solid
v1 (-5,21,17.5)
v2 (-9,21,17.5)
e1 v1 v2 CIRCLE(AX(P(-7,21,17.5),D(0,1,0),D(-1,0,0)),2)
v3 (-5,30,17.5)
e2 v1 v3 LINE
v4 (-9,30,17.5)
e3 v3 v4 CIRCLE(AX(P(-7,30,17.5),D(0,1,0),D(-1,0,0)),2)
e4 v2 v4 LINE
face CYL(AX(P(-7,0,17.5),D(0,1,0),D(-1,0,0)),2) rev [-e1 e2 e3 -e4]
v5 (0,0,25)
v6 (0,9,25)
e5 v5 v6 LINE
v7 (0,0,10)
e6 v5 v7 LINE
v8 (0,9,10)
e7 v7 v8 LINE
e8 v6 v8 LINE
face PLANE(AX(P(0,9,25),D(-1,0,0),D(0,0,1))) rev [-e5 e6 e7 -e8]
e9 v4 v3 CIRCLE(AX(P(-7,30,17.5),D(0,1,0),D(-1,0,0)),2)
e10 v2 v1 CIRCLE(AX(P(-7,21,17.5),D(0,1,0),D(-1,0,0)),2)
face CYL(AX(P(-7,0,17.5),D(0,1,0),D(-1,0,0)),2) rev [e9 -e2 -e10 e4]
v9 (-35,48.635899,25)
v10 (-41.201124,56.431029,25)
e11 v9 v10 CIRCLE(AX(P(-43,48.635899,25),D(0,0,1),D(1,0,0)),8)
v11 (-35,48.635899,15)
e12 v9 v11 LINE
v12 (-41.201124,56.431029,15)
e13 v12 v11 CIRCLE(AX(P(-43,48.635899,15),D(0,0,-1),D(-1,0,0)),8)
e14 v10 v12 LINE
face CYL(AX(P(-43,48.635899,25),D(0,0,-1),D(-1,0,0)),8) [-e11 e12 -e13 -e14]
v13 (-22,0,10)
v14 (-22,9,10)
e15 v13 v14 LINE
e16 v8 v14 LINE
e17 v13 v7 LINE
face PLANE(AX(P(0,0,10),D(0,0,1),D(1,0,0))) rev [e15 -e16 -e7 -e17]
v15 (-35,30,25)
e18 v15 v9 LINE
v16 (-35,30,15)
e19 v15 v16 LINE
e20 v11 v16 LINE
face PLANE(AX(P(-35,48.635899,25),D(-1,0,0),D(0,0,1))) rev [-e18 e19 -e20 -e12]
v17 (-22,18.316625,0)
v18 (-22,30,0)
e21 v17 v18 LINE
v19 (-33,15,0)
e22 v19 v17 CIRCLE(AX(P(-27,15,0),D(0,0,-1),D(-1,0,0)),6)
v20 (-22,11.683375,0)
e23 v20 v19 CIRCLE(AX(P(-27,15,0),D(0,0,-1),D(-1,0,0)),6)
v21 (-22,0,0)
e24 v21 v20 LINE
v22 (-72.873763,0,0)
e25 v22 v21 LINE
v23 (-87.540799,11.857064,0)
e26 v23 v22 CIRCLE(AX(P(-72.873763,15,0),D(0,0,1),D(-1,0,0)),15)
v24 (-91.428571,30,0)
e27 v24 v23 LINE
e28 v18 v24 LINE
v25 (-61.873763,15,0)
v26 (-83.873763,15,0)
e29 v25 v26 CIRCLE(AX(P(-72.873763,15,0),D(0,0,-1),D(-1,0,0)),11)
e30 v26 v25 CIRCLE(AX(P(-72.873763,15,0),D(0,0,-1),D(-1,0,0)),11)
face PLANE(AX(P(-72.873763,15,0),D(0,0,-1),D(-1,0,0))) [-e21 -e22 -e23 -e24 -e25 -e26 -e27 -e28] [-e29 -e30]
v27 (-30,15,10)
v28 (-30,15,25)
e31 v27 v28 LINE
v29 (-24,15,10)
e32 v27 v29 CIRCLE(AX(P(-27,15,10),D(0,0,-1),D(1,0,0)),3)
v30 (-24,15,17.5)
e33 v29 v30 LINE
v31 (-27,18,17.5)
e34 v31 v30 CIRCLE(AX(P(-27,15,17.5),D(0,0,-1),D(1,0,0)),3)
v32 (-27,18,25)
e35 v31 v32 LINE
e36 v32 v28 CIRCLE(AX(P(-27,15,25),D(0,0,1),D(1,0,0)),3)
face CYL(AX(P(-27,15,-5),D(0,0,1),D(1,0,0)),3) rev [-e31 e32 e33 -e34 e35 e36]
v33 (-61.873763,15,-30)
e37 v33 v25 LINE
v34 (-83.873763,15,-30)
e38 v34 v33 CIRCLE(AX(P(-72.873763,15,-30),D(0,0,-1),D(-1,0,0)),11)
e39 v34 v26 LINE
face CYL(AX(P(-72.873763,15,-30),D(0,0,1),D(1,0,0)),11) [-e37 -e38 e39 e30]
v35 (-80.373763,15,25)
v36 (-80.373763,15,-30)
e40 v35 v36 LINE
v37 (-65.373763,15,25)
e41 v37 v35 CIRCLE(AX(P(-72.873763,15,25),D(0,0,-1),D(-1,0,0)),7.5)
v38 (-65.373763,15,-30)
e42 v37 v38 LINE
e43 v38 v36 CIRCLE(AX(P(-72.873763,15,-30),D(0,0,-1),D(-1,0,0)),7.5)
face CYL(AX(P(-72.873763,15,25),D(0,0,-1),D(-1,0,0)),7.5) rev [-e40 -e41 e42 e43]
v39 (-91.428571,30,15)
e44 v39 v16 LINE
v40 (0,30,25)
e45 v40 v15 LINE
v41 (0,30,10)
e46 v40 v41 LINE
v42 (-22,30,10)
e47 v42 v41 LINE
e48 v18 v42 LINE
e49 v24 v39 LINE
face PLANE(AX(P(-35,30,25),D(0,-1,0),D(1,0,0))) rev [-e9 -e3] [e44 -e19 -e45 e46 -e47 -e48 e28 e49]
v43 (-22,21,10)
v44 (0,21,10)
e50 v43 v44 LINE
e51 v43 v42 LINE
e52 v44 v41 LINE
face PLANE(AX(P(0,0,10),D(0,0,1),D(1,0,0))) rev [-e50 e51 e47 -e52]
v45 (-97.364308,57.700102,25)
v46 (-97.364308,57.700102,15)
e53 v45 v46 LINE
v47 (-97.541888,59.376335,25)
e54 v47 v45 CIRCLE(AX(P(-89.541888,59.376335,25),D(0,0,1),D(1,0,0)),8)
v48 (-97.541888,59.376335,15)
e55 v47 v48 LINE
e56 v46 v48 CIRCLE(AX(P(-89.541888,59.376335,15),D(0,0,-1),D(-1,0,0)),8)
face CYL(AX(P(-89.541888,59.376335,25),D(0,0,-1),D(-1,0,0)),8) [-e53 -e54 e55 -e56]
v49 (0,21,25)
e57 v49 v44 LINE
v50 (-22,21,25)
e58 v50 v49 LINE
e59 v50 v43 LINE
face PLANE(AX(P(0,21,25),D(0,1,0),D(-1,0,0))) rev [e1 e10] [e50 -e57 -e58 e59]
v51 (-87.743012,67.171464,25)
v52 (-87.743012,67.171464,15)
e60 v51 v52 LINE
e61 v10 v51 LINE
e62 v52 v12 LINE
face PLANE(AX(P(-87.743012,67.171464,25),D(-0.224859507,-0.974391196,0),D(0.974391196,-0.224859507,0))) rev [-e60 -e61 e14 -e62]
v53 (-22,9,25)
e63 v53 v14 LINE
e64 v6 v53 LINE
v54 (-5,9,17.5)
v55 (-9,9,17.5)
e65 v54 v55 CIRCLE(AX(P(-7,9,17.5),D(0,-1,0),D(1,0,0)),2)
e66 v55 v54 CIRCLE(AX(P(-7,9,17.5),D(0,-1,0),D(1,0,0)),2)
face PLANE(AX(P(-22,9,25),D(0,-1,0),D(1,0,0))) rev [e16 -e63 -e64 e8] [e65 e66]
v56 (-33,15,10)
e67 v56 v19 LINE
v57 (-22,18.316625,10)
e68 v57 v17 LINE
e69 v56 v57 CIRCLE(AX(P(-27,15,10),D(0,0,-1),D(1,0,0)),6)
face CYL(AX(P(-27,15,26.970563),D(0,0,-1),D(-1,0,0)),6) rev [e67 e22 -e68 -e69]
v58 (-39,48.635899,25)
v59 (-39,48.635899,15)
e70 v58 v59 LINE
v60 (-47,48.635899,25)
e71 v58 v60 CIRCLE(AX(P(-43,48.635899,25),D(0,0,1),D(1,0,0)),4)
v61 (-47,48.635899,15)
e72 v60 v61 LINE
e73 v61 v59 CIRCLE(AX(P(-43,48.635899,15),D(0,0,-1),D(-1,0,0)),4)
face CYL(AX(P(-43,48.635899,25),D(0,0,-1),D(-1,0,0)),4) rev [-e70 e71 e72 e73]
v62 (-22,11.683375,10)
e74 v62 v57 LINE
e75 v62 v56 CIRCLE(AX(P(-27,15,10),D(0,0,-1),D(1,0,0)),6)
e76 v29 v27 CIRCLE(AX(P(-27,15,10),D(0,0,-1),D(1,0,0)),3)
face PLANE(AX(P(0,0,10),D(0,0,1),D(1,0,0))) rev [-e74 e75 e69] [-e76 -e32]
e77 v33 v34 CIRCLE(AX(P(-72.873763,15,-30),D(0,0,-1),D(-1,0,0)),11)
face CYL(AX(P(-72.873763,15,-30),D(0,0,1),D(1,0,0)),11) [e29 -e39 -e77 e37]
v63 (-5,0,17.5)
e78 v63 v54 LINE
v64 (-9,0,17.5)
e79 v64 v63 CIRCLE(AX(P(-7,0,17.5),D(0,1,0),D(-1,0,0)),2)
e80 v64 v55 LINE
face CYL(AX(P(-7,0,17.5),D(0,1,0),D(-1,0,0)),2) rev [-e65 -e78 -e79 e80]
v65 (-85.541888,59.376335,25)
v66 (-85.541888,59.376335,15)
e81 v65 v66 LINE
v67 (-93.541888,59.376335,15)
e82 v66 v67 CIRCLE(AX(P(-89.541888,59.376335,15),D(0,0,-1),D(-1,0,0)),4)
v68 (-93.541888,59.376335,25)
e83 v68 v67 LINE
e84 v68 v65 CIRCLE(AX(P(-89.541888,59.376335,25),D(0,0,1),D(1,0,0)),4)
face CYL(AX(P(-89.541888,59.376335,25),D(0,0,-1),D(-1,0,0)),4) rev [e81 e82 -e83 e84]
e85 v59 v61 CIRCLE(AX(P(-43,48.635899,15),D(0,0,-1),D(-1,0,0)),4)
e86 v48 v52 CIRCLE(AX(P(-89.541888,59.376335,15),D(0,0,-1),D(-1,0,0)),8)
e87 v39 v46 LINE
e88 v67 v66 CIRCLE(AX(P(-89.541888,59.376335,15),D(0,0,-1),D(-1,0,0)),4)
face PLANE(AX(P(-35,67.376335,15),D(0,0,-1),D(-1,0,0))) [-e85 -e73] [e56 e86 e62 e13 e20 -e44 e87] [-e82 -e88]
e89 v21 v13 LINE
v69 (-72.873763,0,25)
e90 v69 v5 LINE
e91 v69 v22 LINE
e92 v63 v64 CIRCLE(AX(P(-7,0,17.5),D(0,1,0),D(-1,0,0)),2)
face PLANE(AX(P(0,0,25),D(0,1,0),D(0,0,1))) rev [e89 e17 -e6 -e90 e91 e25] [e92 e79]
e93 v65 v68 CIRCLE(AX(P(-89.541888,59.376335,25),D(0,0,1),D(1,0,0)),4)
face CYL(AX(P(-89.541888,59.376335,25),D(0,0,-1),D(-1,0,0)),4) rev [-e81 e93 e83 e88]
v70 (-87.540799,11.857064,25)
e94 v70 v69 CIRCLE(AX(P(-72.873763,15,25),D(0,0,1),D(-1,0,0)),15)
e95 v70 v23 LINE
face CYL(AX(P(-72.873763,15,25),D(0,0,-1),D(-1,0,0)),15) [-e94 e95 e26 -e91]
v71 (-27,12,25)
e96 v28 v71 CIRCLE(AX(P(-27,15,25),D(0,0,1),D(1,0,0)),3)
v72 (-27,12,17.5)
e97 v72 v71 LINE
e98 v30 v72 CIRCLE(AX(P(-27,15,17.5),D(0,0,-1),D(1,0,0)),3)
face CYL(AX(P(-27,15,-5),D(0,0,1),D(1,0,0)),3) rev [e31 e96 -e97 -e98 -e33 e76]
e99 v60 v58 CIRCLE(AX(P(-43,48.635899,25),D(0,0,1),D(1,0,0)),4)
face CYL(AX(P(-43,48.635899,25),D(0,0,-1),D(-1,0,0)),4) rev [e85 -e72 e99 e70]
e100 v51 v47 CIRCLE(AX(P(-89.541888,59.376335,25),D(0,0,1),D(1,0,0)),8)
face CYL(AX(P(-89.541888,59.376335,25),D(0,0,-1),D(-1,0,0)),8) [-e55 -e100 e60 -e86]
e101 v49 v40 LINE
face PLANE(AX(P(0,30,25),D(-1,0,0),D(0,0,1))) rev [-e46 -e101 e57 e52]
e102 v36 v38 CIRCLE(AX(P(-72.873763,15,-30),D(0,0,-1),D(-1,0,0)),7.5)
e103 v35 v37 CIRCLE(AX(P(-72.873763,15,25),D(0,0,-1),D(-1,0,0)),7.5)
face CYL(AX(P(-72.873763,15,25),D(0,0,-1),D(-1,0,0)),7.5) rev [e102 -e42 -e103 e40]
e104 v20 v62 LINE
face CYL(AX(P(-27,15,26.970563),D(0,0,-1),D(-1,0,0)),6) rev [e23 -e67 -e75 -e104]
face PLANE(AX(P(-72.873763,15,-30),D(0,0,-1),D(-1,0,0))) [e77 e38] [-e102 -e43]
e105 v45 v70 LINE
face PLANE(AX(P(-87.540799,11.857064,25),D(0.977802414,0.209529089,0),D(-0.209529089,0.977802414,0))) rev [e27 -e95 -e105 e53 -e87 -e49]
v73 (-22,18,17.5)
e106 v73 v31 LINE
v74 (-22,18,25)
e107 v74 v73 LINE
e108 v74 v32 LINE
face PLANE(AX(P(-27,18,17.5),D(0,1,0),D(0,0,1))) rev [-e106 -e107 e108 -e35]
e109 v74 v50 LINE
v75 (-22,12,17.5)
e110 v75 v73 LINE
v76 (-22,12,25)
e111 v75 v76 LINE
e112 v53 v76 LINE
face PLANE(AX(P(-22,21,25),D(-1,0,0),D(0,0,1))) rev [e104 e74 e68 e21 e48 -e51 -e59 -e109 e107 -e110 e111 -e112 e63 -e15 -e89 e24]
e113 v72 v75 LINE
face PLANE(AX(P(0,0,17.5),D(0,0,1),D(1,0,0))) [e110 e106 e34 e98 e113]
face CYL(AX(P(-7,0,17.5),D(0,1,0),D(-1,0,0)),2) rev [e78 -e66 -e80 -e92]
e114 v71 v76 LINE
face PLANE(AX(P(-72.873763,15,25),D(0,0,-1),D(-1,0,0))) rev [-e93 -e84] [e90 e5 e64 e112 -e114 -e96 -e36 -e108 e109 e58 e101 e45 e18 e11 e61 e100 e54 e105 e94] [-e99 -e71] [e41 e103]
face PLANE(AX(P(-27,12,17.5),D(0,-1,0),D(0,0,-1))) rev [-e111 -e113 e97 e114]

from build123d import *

# Parameters (mm, degrees)
BRACKET_PLATE_PROFILE_R     = 4
BRACKET_PLATE_DEPTH         = 25
FORK_SLOT_SKETCH_W          = 80.7543585
FORK_SLOT_SKETCH_H          = 21.257894267
FORK_SLOT_DEPTH             = 108.407683018
PIVOT_BOSS_SKETCH_R         = 11
PIVOT_BOSS_22_DEPTH         = 30
PIVOT_BORE_SKETCH_R         = 7.5
PIVOT_BORE_15_DEPTH         = 131.686611628
FORK_NOTCH_SKETCH_W         = 22
FORK_NOTCH_SKETCH_H         = 19.498267172
FORK_NOTCH_22X10_DEPTH      = 109.680312712
FORK_PIN_HOLE_SKETCH_R      = 2
FORK_PIN_HOLE_DEPTH         = 30
CLAMP_HOLE_SKETCH_R         = 3
CLAMP_HOLE_DEPTH            = 30
CLAMP_POCKET_SKETCH_W       = 7.221877003
CLAMP_POCKET_SKETCH_H       = 6
CLAMP_POCKET_7_5_DEEP_DEPTH = 7.5
HOLE_12_SKETCH_R            = 6
HOLE_12_DEPTH               = 10


with BuildPart() as part:
    # Bracket Plate Profile → Bracket Plate (new body)
    with BuildSketch(Plane.XY):
        with BuildLine():
            Line((0, 0), (-72.873763146, 0))
            ThreePointArc((-72.873763146, 0), (-82.303926322, 3.335008681), (-87.540799358, 11.857063669))
            Line((-87.540799358, 11.857063669), (-97.364307589, 57.700102084))
            ThreePointArc((-97.364307589, 57.700102084), (-95.154146662, 65.077436074), (-87.743012223, 67.171464359))
            Line((-87.743012223, 67.171464359), (-41.201123946, 56.431028603))
            ThreePointArc((-41.201123946, 56.431028603), (-36.739368705, 53.616310244), (-35, 48.635899037))
            Line((-35, 48.635899037), (-35, 30))
            Line((-35, 30), (0, 30))
            Line((0, 30), (0, 21))
            Line((0, 21), (-22, 21))
            Line((-22, 21), (-22, 9))
            Line((-22, 9), (0, 9))
            Line((0, 9), (0, 0))
        make_face()
        with Locations((-89.541888277, 59.376334794)):
            Circle(BRACKET_PLATE_PROFILE_R, mode=Mode.SUBTRACT)
        with Locations((-43, 48.635899037)):
            Circle(BRACKET_PLATE_PROFILE_R, mode=Mode.SUBTRACT)
    extrude(amount=BRACKET_PLATE_DEPTH)

    # Fork Slot Sketch → Fork Slot (cut, through all)
    with BuildSketch(Plane(origin=(0, 30, 0), x_dir=(1, 0, 0), z_dir=(0, 1, 0))):
        with Locations((-75.37717925, -4.371052867)):
            Rectangle(FORK_SLOT_SKETCH_W, FORK_SLOT_SKETCH_H)
    extrude(amount=FORK_SLOT_DEPTH, mode=Mode.SUBTRACT)

    # Pivot Boss Sketch → Pivot Boss Ø22 (add)
    with BuildSketch(Plane(origin=(0, 0, 0), x_dir=(-1, 0, 0), z_dir=(0, 0, -1))):
        with Locations((72.873763146, 15)):
            Circle(PIVOT_BOSS_SKETCH_R)
    extrude(amount=PIVOT_BOSS_22_DEPTH)

    # Pivot Bore Sketch → Pivot Bore Ø15 (cut, through all)
    with BuildSketch(Plane(origin=(0, 0, -30), x_dir=(-1, 0, 0), z_dir=(0, 0, -1))):
        with Locations((72.873763146, 15)):
            Circle(PIVOT_BORE_SKETCH_R)
    extrude(amount=-PIVOT_BORE_15_DEPTH, mode=Mode.SUBTRACT)

    # Fork Notch Sketch → Fork Notch 22x10 (cut, through all)
    with BuildSketch(Plane(origin=(0, 30, 0), x_dir=(1, 0, 0), z_dir=(0, 1, 0))):
        with Locations((-11, -0.250866414)):
            Rectangle(FORK_NOTCH_SKETCH_W, FORK_NOTCH_SKETCH_H)
    extrude(amount=-FORK_NOTCH_22X10_DEPTH, mode=Mode.SUBTRACT)

    # Fork Pin Hole Sketch → Fork Pin Hole (cut)
    with BuildSketch(Plane(origin=(0, 30, 0), x_dir=(1, 0, 0), z_dir=(0, 1, 0))):
        with Locations(Location((-7, -17.5, 0), (0, 0, 180))):
            Circle(FORK_PIN_HOLE_SKETCH_R)
    extrude(amount=-FORK_PIN_HOLE_DEPTH, mode=Mode.SUBTRACT)

    # Clamp Hole Sketch → Clamp Hole (cut)
    with BuildSketch(Plane.XY.offset(25)):
        with Locations((-27, 15)):
            Circle(CLAMP_HOLE_SKETCH_R)
    extrude(amount=-CLAMP_HOLE_DEPTH, mode=Mode.SUBTRACT)

    # Clamp Pocket Sketch → Clamp Pocket 7.5 Deep (cut)
    with BuildSketch(Plane.XY.offset(25)):
        with Locations((-23.389061498, 15)):
            Rectangle(CLAMP_POCKET_SKETCH_W, CLAMP_POCKET_SKETCH_H)
    extrude(amount=-CLAMP_POCKET_7_5_DEEP_DEPTH, mode=Mode.SUBTRACT)

    # Hole Ø12 Sketch → Hole Ø12 (cut)
    with BuildSketch(Plane(origin=(0, 0, 0), x_dir=(-1, 0, 0), z_dir=(0, 0, -1))):
        with Locations((27, 15)):
            Circle(HOLE_12_SKETCH_R)
    extrude(amount=-HOLE_12_DEPTH, mode=Mode.SUBTRACT)


solid = part.part
